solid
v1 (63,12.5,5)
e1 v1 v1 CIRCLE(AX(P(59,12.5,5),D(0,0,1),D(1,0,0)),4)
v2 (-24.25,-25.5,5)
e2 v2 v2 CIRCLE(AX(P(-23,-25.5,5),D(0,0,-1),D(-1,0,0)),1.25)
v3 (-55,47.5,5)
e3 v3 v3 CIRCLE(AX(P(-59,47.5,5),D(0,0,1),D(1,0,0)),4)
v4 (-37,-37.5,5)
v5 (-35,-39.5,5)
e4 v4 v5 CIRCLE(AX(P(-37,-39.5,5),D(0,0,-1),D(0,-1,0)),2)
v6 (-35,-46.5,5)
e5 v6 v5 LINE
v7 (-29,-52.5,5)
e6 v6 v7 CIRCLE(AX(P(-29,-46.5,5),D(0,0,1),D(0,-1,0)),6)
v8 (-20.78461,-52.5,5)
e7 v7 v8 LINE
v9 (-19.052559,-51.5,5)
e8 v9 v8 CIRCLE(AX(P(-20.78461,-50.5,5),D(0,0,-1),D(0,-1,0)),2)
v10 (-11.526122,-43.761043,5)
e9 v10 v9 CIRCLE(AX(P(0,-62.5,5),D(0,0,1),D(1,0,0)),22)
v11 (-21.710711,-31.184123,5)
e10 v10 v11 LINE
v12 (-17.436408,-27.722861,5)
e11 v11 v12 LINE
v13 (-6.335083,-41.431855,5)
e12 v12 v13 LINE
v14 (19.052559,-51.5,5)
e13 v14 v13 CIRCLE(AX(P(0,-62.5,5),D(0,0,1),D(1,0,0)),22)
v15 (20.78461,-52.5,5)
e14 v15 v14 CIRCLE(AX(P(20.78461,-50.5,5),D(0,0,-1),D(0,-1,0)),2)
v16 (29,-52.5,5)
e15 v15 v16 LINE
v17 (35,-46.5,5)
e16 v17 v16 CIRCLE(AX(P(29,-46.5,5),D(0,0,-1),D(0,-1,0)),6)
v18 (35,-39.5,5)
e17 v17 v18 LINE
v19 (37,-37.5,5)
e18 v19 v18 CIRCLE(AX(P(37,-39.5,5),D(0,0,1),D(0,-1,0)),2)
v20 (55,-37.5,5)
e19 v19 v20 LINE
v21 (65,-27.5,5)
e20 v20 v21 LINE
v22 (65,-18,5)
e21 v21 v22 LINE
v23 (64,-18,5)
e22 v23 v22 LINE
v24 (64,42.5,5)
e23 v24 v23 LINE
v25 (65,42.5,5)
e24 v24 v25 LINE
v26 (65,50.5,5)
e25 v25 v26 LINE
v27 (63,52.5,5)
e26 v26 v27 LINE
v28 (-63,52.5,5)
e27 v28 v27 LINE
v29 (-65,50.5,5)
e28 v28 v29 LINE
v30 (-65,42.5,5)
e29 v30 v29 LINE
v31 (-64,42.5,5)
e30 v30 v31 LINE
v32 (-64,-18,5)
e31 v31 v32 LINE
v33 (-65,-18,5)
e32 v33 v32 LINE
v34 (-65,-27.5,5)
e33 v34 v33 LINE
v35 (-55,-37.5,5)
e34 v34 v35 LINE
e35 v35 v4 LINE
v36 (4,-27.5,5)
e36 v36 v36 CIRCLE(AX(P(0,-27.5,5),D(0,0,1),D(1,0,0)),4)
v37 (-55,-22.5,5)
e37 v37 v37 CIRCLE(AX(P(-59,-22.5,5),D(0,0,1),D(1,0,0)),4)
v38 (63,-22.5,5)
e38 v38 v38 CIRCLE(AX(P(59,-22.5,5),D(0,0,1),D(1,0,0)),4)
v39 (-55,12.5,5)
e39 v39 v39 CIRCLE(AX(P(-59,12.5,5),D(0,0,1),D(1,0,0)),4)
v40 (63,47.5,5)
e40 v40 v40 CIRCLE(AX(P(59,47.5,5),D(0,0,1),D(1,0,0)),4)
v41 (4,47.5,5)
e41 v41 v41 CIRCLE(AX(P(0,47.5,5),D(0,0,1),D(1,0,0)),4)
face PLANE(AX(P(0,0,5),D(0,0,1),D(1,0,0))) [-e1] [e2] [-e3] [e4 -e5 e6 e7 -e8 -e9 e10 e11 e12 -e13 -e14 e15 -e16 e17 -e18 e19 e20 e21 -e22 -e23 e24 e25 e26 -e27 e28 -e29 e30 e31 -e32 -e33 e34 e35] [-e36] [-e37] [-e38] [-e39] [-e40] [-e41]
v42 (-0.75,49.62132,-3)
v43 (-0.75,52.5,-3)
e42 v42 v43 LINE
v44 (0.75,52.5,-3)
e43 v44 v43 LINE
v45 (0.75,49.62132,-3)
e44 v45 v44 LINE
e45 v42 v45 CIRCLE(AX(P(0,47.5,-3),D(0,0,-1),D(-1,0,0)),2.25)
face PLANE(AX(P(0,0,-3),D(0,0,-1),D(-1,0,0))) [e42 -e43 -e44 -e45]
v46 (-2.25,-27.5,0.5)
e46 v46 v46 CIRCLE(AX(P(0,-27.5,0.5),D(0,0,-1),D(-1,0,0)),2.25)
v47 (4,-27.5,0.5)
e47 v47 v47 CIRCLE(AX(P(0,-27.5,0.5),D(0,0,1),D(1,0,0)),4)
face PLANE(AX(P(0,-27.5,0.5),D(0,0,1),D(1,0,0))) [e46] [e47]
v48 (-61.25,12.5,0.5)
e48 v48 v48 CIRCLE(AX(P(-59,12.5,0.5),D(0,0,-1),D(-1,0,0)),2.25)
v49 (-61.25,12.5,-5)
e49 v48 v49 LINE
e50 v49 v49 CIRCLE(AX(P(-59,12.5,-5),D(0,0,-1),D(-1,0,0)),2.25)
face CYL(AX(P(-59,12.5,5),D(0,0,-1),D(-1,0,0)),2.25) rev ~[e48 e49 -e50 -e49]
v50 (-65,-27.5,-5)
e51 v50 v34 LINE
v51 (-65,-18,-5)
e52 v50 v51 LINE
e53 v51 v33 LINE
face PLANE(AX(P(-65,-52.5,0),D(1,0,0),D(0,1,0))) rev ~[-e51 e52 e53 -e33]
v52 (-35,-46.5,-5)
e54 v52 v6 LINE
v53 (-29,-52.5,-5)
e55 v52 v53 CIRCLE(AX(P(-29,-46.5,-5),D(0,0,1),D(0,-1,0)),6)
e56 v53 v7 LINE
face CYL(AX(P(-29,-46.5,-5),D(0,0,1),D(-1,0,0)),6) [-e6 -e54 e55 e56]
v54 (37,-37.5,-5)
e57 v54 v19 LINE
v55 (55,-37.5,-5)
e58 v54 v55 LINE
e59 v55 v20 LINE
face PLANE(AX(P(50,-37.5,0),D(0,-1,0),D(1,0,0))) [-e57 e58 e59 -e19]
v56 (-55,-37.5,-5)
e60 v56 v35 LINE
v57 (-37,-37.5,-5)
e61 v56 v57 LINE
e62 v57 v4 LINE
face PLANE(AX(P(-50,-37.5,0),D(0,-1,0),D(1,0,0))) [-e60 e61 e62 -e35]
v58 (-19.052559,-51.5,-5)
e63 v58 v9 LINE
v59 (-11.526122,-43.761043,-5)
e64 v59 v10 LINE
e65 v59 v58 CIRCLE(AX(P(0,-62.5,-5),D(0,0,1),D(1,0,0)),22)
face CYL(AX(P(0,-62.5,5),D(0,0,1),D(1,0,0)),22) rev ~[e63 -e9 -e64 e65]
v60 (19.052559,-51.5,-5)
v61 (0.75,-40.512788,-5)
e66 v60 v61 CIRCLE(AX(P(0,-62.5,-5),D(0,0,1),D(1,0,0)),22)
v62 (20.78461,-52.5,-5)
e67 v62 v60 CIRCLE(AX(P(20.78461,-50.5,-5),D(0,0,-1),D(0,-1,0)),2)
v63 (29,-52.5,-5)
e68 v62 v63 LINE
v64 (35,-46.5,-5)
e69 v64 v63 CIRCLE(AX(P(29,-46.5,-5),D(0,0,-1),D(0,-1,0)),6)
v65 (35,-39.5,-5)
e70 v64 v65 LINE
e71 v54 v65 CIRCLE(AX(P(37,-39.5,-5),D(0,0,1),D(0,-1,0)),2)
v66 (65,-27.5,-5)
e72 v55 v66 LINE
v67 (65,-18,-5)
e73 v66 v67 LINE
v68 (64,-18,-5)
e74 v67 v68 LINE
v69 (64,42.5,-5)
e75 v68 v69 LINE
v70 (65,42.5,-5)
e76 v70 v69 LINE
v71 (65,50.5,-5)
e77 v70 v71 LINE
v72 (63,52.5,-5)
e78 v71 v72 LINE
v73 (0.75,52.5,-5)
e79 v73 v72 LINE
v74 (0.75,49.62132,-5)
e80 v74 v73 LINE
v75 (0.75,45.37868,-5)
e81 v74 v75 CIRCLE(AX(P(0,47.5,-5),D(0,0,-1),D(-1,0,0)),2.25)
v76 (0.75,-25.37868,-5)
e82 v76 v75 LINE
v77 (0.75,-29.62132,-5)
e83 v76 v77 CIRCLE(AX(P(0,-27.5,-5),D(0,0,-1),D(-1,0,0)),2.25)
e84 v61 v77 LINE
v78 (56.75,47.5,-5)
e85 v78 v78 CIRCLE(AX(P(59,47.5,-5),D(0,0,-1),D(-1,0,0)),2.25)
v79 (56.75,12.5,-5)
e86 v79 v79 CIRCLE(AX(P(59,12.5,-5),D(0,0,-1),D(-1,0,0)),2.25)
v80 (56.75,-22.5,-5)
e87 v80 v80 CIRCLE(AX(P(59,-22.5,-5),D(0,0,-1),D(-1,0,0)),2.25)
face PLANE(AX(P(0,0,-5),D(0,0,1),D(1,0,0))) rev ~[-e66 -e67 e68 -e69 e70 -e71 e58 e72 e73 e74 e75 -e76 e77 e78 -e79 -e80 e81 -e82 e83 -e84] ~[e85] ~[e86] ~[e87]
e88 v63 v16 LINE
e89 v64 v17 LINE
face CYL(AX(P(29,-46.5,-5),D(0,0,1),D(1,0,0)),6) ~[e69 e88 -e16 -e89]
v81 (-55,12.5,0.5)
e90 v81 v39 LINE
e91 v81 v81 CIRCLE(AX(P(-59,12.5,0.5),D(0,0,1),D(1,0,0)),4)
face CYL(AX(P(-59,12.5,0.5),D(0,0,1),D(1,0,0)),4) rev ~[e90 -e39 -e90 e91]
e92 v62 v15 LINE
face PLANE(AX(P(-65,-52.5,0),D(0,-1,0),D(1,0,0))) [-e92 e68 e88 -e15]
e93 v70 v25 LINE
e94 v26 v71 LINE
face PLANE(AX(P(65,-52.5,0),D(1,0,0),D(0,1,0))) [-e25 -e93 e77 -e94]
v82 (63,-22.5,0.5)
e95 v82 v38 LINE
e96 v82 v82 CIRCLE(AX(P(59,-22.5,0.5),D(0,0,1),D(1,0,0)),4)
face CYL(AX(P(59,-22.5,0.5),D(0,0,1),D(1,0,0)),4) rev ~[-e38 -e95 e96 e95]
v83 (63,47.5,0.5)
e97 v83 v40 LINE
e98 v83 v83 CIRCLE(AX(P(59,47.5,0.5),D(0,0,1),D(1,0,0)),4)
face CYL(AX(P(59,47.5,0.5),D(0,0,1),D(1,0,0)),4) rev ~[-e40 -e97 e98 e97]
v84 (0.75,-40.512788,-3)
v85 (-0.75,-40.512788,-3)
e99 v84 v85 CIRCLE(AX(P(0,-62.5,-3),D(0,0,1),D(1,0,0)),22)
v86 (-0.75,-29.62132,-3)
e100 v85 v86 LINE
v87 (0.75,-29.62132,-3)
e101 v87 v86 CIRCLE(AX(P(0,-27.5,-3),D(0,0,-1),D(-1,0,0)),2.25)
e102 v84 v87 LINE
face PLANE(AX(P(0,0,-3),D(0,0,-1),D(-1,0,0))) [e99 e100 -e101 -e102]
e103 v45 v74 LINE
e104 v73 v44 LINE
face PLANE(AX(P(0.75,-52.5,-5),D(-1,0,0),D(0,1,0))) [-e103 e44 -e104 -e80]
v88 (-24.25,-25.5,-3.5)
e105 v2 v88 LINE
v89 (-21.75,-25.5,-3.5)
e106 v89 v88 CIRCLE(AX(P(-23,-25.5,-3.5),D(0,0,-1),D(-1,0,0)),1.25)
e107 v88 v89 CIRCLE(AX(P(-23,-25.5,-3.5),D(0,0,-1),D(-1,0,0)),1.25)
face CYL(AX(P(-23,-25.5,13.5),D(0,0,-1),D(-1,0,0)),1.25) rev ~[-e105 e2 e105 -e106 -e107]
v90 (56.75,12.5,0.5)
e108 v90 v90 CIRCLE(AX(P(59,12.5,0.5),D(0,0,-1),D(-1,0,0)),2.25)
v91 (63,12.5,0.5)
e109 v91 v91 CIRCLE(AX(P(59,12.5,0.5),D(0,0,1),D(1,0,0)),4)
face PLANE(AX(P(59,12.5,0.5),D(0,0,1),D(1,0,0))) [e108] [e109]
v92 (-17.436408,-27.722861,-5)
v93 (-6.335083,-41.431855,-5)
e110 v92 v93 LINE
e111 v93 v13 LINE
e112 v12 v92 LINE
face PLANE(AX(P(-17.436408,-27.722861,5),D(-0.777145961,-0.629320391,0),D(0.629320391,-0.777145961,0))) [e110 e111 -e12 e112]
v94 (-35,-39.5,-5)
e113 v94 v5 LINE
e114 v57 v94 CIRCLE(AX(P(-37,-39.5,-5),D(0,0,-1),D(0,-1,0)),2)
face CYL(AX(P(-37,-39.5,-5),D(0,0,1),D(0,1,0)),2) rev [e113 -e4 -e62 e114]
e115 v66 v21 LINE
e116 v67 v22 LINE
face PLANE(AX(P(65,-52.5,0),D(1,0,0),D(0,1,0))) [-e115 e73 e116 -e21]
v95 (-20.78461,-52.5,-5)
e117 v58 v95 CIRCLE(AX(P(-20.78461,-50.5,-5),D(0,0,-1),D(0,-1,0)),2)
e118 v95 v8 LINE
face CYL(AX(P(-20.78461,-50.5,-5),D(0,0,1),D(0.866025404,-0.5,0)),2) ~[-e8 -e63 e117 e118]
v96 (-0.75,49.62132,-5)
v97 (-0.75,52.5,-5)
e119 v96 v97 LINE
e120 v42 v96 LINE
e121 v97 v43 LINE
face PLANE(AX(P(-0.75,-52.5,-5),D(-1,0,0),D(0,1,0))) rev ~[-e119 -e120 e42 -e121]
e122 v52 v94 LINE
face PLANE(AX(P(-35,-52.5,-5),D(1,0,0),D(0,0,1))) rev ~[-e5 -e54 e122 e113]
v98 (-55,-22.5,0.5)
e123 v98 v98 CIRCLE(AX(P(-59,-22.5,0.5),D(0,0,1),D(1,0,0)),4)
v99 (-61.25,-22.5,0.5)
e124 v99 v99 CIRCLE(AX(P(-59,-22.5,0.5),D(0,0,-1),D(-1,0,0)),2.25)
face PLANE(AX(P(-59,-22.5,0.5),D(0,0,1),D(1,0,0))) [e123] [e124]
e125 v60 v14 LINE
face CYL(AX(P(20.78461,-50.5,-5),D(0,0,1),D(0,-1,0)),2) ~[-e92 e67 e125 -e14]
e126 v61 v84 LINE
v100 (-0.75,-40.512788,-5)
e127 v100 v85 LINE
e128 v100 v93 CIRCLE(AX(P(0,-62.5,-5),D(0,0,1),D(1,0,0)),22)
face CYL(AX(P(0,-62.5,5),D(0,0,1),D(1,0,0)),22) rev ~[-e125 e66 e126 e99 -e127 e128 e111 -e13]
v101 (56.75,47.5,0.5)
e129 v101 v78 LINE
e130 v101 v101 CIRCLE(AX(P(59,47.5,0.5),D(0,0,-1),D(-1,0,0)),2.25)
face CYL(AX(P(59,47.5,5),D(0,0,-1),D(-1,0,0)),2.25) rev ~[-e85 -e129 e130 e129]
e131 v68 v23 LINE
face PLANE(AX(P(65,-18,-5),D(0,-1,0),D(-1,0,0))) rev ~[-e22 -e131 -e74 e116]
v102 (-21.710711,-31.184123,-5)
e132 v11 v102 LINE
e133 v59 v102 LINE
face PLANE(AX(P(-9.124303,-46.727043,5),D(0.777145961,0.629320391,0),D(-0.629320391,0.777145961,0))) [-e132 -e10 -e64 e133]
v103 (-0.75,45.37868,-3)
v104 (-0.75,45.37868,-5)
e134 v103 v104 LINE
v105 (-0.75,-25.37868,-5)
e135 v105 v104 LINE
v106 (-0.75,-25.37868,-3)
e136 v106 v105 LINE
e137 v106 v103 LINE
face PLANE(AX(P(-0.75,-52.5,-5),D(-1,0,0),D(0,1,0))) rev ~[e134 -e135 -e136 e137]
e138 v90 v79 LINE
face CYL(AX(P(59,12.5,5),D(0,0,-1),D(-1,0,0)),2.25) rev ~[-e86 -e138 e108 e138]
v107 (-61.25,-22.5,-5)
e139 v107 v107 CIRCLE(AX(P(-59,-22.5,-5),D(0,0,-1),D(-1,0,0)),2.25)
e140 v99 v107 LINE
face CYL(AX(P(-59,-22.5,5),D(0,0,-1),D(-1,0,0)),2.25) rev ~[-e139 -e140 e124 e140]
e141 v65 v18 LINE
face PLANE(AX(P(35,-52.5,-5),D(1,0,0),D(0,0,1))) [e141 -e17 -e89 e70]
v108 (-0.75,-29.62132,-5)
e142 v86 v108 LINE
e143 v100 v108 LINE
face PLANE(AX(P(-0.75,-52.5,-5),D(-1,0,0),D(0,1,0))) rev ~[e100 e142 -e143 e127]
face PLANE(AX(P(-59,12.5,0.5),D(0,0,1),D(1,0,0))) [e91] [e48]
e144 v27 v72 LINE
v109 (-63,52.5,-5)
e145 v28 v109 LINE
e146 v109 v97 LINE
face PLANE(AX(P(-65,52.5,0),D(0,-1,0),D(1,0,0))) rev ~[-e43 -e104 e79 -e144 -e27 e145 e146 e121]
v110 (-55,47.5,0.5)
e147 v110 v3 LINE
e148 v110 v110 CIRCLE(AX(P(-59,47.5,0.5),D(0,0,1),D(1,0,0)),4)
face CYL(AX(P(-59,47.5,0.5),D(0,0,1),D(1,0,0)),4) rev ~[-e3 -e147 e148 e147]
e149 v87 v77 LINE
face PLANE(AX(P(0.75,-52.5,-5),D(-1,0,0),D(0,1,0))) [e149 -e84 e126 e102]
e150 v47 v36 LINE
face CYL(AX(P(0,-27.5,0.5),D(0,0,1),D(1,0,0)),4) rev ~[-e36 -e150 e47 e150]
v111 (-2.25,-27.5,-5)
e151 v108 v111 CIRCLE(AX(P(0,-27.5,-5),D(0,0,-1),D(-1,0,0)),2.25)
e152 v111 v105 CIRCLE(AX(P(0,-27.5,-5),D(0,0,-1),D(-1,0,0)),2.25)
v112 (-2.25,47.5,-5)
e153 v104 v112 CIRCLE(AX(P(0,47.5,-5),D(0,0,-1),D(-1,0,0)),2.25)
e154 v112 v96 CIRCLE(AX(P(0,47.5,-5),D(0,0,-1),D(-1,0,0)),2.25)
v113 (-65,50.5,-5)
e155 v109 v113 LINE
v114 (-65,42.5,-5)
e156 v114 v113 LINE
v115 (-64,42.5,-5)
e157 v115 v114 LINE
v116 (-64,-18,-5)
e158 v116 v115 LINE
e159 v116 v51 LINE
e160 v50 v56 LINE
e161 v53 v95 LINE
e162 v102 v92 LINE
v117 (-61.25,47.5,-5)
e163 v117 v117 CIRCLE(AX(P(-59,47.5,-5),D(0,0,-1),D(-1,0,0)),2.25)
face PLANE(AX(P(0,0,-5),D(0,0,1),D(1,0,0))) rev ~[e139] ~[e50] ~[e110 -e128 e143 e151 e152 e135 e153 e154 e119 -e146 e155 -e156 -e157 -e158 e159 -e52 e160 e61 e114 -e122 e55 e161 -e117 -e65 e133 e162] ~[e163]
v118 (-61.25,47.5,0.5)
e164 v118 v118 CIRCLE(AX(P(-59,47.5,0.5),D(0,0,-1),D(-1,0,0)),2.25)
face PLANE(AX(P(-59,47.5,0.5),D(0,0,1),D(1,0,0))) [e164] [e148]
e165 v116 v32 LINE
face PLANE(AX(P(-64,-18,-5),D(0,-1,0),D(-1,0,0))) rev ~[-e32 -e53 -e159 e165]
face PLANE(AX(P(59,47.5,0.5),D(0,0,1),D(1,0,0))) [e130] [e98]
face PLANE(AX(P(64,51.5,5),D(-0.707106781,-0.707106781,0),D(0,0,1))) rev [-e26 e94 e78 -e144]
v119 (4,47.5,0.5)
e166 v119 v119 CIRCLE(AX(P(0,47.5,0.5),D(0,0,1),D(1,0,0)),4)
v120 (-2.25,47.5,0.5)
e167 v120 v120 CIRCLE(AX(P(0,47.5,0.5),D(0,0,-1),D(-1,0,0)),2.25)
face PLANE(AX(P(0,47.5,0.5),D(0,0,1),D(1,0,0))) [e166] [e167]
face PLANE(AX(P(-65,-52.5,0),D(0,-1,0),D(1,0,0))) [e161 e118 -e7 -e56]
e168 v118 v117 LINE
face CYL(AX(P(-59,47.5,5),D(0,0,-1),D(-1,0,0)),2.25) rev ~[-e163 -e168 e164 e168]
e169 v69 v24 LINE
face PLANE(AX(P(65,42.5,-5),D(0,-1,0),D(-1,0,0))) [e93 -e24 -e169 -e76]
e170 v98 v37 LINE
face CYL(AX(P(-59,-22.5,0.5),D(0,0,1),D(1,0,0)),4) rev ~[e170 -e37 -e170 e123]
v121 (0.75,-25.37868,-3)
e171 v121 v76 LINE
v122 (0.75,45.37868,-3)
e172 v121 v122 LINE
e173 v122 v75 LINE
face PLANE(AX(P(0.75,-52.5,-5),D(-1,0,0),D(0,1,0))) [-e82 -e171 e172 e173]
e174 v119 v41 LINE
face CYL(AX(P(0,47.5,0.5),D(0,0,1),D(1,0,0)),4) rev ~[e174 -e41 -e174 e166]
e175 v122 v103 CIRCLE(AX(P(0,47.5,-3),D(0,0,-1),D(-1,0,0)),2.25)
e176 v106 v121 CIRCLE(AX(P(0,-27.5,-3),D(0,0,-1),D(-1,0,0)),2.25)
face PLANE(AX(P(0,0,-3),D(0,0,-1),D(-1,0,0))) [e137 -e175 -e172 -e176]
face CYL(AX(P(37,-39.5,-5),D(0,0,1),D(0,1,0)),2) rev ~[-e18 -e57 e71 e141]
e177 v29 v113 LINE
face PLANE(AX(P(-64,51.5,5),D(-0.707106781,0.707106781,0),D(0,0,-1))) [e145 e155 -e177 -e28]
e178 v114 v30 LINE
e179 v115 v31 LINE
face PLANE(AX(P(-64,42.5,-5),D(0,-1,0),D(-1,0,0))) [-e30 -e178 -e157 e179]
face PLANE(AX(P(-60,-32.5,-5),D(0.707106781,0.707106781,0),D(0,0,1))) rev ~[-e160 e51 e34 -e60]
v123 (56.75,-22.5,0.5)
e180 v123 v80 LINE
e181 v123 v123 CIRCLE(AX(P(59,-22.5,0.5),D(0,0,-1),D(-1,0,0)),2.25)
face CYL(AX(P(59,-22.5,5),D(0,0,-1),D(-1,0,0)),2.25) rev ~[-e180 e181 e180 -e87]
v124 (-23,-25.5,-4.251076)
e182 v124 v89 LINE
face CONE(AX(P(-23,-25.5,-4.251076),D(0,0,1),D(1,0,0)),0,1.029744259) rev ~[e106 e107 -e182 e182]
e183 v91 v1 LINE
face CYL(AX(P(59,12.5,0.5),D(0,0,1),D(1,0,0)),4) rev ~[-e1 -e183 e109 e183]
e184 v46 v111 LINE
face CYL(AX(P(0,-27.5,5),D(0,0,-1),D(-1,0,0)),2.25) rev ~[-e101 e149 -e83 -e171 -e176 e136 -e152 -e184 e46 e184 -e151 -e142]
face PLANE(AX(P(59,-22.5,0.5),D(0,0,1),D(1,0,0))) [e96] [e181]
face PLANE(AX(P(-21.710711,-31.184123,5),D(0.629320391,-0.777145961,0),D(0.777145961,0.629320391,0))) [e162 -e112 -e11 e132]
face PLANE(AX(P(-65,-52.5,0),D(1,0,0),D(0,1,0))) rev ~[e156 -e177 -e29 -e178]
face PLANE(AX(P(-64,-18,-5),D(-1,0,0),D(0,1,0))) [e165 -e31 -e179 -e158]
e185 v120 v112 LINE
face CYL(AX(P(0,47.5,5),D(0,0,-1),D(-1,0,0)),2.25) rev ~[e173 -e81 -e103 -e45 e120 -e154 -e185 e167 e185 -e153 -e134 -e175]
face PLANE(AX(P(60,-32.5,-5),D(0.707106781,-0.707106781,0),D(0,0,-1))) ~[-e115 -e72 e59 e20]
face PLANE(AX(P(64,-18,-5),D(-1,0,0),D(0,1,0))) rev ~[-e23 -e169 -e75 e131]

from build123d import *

# Parameters (mm, degrees)
SKETCH1_W                                            = 130
SKETCH1_H                                            = 105
BOSS_EXTRUDE1_DEPTH                                  = 5
SKETCH3_R                                            = 22
CUT_EXTRUDE2_DEPTH                                   = 85.150163399
SKETCH7_W                                            = 30
SKETCH7_H                                            = 10
CUT_EXTRUDE5_DEPTH                                   = 15
FILLET1_R                                            = 6
CHAMFER1_SIZE                                        = 10
FILLET2_R                                            = 2
CUT_EXTRUDE8_DEPTH                                   = 85.150163399
FILLET3_R                                            = 2
CHAMFER2_SIZE                                        = 2
SKETCH15_W                                           = 1
SKETCH15_H                                           = 60.5
CUT_EXTRUDE10_DEPTH                                  = 85.150163399
HOLE_SIZE_PER_SOCKET_HEAD_CAP_SCREW_TYPE_D           = 4.5
HOLE_SIZE_PER_SOCKET_HEAD_CAP_SCREW_TYPE_CBORE_D     = 8
HOLE_SIZE_PER_SOCKET_HEAD_CAP_SCREW_TYPE_CBORE_DEPTH = 4.5
M3_TAPPED_HOLE1_D                                    = 2.5
M3_TAPPED_HOLE1_DEPTH                                = 8.5
M3_TAPPED_HOLE1_TIP                                  = 0.751075774
SKETCH20_W                                           = 1.5
SKETCH20_H                                           = 105
CUT_EXTRUDE11_DEPTH                                  = 2


with BuildPart() as part:
    # Sketch1 → Boss-Extrude1 (new, symmetric)
    with BuildSketch(Plane.XY):
        Rectangle(SKETCH1_W, SKETCH1_H)
    extrude(amount=BOSS_EXTRUDE1_DEPTH, both=True)

    # Sketch3 → Cut-Extrude2 (cut, through all)
    with BuildSketch(Plane.XY.offset(5)):
        with Locations((0, -62.5)):
            Circle(SKETCH3_R)
    extrude(amount=-CUT_EXTRUDE2_DEPTH, mode=Mode.SUBTRACT)

    # Sketch7 → Cut-Extrude5 (cut)
    with BuildSketch(Plane.XZ.offset(52.5)):
        with Locations((-50, 0)):
            Rectangle(SKETCH7_W, SKETCH7_H)
        with Locations((50, 0)):
            Rectangle(SKETCH7_W, SKETCH7_H)
    extrude(amount=-CUT_EXTRUDE5_DEPTH, mode=Mode.SUBTRACT)

    # Fillet1
    fillet1_edges = [part.edges().sort_by_distance(p)[0] for p in [
        (-35, -52.5, 0),
        (35, -52.5, 0),
    ]]
    fillet(fillet1_edges, radius=FILLET1_R)

    # Chamfer1
    chamfer1_edges = [part.edges().sort_by_distance(p)[0] for p in [
        (-65, -37.5, 0),
        (65, -37.5, 0),
    ]]
    chamfer(chamfer1_edges, length=CHAMFER1_SIZE)

    # Fillet2
    fillet2_edges = [part.edges().sort_by_distance(p)[0] for p in [
        (-35, -37.5, 0),
        (35, -37.5, 0),
    ]]
    fillet(fillet2_edges, radius=FILLET2_R)

    # Sketch10 → Cut-Extrude8 (cut, through all)
    with BuildSketch(Plane.XY.offset(5)):
        Polygon((-21.710710609, -31.184123297), (-17.436407821, -27.722861146), (-4.85, -43.265780375), (-9.124302788, -46.727042526), align=None)
    extrude(amount=-CUT_EXTRUDE8_DEPTH, mode=Mode.SUBTRACT)

    # Fillet3
    fillet3_edges = [part.edges().sort_by_distance(p)[0] for p in [
        (-19.595917942, -52.5, 0),
        (19.595917942, -52.5, 0),
    ]]
    fillet(fillet3_edges, radius=FILLET3_R)

    # Chamfer2
    chamfer2_edges = [part.edges().sort_by_distance(p)[0] for p in [
        (-65, 52.5, 0),
        (65, 52.5, 0),
    ]]
    chamfer(chamfer2_edges, length=CHAMFER2_SIZE)

    # Sketch15 → Cut-Extrude10 (cut, through all)
    with BuildSketch(Plane(origin=(0, 0, -5), x_dir=(-1, 0, 0), z_dir=(0, 0, -1))):
        with Locations((-64.5, 12.25)):
            Rectangle(SKETCH15_W, SKETCH15_H)
        with Locations((64.5, 12.25)):
            Rectangle(SKETCH15_W, SKETCH15_H)
    extrude(amount=-CUT_EXTRUDE10_DEPTH, mode=Mode.SUBTRACT)

    # Hole size per socket head cap screw type 0 (through all)
    with Locations(Plane.XY.offset(5)):
        with Locations((59, 47.5), (0, 47.5), (-59, 47.5), (-59, 12.5), (-59, -22.5), (0, -27.5), (59, -22.5), (59, 12.5)):
            CounterBoreHole(HOLE_SIZE_PER_SOCKET_HEAD_CAP_SCREW_TYPE_D / 2, HOLE_SIZE_PER_SOCKET_HEAD_CAP_SCREW_TYPE_CBORE_D / 2, HOLE_SIZE_PER_SOCKET_HEAD_CAP_SCREW_TYPE_CBORE_DEPTH)

    # M3 Tapped Hole1
    with Locations(Plane.XY.offset(5)):
        with Locations((-23, -25.5)):
            Hole(M3_TAPPED_HOLE1_D / 2, depth=M3_TAPPED_HOLE1_DEPTH)
            with Locations((0, 0, -(M3_TAPPED_HOLE1_DEPTH + M3_TAPPED_HOLE1_TIP / 2))):  # 118° drill point
                Cone(0, M3_TAPPED_HOLE1_D / 2, M3_TAPPED_HOLE1_TIP, mode=Mode.SUBTRACT)

    # Sketch20 → Cut-Extrude11 (cut)
    with BuildSketch(Plane(origin=(0, 0, -5), x_dir=(-1, 0, 0), z_dir=(0, 0, -1))):
        Rectangle(SKETCH20_W, SKETCH20_H)
    extrude(amount=-CUT_EXTRUDE11_DEPTH, mode=Mode.SUBTRACT)


solid = part.part
